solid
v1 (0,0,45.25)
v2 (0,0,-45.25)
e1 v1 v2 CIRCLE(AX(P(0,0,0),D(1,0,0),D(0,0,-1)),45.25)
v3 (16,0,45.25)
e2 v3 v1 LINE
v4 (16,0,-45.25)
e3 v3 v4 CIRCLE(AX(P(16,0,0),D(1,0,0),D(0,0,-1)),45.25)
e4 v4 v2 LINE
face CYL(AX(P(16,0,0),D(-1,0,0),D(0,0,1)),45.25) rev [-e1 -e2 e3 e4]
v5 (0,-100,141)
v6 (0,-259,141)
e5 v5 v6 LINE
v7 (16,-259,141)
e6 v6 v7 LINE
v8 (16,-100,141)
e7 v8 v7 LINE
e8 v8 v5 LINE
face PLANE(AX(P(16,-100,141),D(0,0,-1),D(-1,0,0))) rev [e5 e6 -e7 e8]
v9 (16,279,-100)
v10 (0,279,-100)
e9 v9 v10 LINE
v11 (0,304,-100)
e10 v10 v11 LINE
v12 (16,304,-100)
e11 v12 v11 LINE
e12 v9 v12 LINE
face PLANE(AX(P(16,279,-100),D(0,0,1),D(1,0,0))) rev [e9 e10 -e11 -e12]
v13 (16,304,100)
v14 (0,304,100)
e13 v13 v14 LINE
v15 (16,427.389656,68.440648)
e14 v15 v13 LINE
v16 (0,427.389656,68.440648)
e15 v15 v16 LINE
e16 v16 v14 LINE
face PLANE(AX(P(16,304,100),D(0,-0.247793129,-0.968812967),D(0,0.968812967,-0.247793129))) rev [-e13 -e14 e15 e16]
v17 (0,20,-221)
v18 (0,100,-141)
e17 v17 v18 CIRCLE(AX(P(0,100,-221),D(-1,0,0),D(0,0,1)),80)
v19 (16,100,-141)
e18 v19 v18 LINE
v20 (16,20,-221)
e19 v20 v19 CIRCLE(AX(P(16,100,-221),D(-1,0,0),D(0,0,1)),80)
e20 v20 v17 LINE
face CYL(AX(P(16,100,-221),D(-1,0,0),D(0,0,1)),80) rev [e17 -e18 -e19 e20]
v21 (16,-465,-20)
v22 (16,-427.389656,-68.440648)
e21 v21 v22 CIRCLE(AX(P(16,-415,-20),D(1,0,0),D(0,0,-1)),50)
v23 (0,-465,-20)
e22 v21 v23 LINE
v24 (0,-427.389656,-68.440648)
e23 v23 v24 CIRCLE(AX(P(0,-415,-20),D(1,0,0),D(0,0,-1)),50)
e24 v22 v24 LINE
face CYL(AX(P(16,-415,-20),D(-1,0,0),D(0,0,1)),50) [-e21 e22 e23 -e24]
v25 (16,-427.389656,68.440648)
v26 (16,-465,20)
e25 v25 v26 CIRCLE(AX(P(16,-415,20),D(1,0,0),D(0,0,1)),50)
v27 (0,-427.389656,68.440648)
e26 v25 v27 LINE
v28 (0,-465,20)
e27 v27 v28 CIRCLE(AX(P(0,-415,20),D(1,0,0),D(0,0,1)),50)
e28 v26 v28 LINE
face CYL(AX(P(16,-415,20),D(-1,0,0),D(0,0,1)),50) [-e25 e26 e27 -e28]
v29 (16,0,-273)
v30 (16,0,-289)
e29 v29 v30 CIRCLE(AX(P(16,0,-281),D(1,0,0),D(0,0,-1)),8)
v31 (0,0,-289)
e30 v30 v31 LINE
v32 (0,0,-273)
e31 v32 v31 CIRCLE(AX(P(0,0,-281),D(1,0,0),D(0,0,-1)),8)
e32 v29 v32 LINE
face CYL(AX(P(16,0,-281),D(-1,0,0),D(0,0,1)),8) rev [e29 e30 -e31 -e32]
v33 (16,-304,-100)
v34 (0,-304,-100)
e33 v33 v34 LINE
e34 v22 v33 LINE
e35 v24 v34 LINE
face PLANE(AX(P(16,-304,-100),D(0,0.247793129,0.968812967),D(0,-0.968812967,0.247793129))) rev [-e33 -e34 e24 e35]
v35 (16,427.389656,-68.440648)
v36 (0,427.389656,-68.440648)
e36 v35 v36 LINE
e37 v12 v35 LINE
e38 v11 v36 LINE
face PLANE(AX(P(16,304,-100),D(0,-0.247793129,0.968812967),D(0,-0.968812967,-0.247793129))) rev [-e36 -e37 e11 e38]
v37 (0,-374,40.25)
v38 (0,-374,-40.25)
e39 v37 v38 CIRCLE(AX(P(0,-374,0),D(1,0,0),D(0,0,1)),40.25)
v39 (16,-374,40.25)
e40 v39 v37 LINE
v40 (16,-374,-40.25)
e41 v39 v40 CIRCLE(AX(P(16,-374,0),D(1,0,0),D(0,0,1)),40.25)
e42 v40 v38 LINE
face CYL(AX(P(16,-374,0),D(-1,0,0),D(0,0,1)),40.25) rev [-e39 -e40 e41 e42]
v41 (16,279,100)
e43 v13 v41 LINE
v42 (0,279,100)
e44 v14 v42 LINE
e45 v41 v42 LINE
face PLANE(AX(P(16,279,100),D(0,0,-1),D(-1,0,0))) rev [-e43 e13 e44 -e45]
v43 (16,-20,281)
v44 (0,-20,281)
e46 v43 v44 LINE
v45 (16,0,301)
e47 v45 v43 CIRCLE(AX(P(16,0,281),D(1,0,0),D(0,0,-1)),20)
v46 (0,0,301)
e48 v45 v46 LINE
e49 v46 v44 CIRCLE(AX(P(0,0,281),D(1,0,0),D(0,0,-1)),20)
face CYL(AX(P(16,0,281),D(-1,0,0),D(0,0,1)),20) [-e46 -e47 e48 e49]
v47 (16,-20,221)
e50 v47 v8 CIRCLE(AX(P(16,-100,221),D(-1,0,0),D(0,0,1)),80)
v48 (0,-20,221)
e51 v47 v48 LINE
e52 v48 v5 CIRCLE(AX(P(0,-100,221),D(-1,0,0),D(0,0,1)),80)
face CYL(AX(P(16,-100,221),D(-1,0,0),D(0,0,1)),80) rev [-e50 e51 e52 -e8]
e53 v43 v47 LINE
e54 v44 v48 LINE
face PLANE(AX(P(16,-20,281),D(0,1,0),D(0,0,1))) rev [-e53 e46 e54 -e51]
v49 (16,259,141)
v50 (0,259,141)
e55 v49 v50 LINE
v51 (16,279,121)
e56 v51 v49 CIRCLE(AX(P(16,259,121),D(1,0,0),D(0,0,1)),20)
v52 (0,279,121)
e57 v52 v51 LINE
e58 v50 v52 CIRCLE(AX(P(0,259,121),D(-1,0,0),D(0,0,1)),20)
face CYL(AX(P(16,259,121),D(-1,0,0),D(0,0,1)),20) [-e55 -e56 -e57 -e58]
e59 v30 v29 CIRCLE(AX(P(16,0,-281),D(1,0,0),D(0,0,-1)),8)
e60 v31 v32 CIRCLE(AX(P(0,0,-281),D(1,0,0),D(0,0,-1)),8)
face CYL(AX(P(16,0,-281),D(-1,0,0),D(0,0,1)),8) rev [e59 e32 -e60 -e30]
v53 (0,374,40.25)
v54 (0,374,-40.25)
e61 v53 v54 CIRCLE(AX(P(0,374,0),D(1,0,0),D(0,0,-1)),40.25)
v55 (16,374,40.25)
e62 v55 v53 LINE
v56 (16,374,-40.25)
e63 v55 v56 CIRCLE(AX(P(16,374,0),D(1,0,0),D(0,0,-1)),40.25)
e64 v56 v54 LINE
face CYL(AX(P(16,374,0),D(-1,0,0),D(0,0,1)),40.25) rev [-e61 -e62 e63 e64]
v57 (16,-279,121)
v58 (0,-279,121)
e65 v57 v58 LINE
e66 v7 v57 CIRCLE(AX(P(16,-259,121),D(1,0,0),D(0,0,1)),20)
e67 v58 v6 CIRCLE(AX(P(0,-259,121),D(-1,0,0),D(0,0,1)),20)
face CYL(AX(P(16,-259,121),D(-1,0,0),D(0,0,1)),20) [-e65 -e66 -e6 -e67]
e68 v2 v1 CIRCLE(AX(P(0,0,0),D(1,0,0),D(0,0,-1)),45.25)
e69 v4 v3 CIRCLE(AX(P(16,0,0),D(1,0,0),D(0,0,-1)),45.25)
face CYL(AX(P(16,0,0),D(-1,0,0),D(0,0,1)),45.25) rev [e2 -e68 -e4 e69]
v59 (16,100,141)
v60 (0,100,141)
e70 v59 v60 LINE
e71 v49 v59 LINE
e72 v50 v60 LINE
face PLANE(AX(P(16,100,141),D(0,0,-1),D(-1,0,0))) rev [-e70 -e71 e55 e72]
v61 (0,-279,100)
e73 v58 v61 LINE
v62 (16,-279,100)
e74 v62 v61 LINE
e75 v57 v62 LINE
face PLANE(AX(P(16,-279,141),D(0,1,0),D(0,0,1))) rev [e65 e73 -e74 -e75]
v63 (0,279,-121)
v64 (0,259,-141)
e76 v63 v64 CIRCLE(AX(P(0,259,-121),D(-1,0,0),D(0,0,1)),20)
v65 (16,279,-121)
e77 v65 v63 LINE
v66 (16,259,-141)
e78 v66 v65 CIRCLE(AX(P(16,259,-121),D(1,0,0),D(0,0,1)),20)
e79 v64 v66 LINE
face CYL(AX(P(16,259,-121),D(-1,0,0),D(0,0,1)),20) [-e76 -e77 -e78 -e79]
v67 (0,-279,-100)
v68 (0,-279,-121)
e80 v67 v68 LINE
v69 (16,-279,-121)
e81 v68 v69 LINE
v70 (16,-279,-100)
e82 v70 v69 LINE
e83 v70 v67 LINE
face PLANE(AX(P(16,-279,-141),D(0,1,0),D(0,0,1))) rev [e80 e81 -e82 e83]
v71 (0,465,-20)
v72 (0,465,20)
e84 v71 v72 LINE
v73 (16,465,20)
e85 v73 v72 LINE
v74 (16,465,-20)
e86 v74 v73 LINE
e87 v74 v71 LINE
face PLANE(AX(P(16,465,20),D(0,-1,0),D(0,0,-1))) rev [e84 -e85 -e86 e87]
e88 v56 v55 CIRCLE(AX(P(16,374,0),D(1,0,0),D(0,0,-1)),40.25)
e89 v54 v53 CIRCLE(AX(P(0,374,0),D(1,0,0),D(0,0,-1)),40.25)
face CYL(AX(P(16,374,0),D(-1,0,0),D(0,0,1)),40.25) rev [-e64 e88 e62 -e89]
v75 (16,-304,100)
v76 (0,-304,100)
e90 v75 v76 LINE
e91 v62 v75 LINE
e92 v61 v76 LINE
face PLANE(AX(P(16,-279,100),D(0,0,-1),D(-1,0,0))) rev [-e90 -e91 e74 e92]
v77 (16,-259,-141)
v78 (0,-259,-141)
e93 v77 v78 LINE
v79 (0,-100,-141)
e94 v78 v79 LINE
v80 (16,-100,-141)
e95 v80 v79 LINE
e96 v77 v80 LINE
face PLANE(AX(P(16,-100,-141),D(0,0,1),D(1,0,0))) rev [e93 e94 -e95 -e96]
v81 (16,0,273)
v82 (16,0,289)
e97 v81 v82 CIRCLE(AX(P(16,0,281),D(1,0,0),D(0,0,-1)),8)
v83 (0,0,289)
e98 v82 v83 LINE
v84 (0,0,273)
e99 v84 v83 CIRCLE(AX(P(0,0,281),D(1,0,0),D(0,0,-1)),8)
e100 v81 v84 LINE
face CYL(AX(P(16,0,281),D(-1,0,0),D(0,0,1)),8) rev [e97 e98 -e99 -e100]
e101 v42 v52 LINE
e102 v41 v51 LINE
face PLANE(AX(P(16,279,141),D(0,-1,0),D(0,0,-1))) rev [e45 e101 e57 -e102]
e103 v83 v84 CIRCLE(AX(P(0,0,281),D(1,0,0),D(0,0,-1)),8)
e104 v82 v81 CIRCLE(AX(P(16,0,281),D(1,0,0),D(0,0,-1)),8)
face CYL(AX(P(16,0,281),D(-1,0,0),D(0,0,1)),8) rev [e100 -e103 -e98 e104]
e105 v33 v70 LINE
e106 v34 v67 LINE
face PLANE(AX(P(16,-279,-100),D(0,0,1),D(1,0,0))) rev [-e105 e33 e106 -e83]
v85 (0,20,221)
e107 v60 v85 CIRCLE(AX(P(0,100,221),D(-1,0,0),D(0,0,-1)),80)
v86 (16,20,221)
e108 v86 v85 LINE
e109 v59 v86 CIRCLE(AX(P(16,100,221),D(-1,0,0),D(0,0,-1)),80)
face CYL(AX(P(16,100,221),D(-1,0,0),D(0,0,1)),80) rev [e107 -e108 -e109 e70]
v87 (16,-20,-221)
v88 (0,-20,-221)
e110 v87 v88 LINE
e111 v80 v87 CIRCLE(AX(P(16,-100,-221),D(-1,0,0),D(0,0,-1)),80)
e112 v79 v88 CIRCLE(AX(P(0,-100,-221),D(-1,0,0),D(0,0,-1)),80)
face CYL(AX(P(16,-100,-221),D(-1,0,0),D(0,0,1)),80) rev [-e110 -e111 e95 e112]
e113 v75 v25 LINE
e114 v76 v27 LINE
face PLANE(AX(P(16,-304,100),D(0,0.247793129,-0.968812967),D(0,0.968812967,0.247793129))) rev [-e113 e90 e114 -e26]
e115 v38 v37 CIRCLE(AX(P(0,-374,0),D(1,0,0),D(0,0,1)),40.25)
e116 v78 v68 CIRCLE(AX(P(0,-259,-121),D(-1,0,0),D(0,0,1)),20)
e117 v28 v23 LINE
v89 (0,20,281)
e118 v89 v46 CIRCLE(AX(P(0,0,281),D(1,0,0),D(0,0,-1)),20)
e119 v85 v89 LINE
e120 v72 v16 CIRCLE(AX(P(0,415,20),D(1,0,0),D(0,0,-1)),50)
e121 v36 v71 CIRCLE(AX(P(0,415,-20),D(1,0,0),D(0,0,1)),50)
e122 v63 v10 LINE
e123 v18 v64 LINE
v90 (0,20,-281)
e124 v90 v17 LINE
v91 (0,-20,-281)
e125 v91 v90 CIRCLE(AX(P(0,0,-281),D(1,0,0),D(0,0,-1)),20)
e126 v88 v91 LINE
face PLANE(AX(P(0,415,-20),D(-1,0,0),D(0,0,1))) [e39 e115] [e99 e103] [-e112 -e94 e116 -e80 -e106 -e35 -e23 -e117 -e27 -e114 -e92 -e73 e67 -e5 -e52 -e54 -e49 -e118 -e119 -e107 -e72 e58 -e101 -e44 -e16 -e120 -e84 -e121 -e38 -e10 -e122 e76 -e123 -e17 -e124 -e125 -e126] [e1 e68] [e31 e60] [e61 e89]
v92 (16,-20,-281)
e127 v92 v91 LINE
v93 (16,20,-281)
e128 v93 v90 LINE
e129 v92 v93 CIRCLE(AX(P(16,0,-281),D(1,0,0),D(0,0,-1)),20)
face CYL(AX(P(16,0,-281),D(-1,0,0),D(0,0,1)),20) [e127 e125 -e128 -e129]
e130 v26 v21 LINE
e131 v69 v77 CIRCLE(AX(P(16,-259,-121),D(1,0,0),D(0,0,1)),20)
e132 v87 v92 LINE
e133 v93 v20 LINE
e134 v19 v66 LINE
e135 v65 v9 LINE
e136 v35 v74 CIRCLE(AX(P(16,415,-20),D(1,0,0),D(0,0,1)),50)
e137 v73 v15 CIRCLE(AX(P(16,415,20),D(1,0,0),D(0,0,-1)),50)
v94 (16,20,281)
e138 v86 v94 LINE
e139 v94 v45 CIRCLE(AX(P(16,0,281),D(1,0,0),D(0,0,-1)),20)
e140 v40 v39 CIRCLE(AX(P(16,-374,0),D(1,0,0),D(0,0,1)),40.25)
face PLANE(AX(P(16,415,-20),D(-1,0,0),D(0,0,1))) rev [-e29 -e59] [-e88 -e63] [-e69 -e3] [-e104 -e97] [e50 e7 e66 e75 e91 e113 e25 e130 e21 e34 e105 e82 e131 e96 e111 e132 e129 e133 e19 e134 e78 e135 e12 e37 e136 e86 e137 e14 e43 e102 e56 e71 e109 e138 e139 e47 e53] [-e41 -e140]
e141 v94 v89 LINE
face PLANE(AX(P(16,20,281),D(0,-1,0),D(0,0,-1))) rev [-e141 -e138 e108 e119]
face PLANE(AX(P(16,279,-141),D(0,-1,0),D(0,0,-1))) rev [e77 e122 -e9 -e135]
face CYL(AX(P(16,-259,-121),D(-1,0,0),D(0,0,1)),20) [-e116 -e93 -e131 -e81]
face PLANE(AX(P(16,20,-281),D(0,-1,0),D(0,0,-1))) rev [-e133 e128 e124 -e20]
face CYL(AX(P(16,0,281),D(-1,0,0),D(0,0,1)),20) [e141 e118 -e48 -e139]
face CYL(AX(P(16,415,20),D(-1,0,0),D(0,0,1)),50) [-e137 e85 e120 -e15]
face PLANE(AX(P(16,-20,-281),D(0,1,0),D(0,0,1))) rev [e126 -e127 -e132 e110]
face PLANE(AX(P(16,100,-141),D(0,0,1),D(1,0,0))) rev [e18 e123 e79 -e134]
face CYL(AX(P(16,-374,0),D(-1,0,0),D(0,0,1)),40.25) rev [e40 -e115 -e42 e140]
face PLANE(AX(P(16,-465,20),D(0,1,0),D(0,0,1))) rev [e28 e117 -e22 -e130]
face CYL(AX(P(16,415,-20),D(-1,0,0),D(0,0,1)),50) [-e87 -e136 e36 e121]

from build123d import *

# Parameters (mm, degrees)
SKETCH1_R           = 40.25
SKETCH1_R_2         = 45.25
SKETCH1_R_3         = 4.25
SKETCH1_R_4         = 3.5
SKETCH1_R_5         = 8
BOSS_EXTRUDE1_DEPTH = 16
FILLET1_R           = 20
SKETCH2_R           = 4.25
SKETCH2_R_2         = 3.5
BOSS_EXTRUDE2_DEPTH = 16


with BuildPart() as part:
    # Sketch1 → Boss-Extrude1 (new body)
    with BuildSketch(Plane(origin=(0, 0, 0), x_dir=(0, 0, -1), z_dir=(1, 0, 0))):
        with BuildLine():
            Line((-281, 20), (-221, 20))
            ThreePointArc((-221, 20), (-164.431457505, 43.431457505), (-141, 100))
            Line((-141, 100), (-141, 279))
            Line((-141, 279), (-100, 279))
            Line((-100, 279), (-100, 304))
            Line((-100, 304), (-68.44064835, 427.389656469))
            ThreePointArc((-68.44064835, 427.389656469), (-50.663636253, 454.493561649), (-20, 465))
            Line((-20, 465), (20, 465))
            ThreePointArc((20, 465), (50.663636253, 454.493561649), (68.44064835, 427.389656469))
            Line((68.44064835, 427.389656469), (100, 304))
            Line((100, 304), (100, 279))
            Line((100, 279), (141, 279))
            Line((141, 279), (141, 100))
            ThreePointArc((141, 100), (164.431457505, 43.431457505), (221, 20))
            Line((221, 20), (281, 20))
            ThreePointArc((281, 20), (301, 0), (281, -20))
            Line((281, -20), (221, -20))
            ThreePointArc((221, -20), (164.431457505, -43.431457505), (141, -100))
            Line((141, -100), (141, -279))
            Line((141, -279), (100, -279))
            Line((100, -279), (100, -304))
            Line((100, -304), (68.44064835, -427.389656469))
            ThreePointArc((68.44064835, -427.389656469), (50.663636253, -454.493561649), (20, -465))
            Line((20, -465), (-20, -465))
            ThreePointArc((-20, -465), (-50.663636253, -454.493561649), (-68.44064835, -427.389656469))
            Line((-68.44064835, -427.389656469), (-100, -304))
            Line((-100, -304), (-100, -279))
            Line((-100, -279), (-141, -279))
            Line((-141, -279), (-141, -100))
            ThreePointArc((-141, -100), (-164.431457505, -43.431457505), (-221, -20))
            Line((-221, -20), (-281, -20))
            ThreePointArc((-281, -20), (-301, 0), (-281, 20))
        make_face()
        with Locations((0, 374)):
            Circle(SKETCH1_R, mode=Mode.SUBTRACT)
        Circle(SKETCH1_R_2, mode=Mode.SUBTRACT)
        with Locations(Location((0, -374, 0), (0, 0, 180))):
            Circle(SKETCH1_R, mode=Mode.SUBTRACT)
        with Locations((20, -75)):
            Circle(SKETCH1_R_3, mode=Mode.SUBTRACT)
        with Locations((-20, -75)):
            Circle(SKETCH1_R_3, mode=Mode.SUBTRACT)
        with Locations((-20, 442)):
            Circle(SKETCH1_R_4, mode=Mode.SUBTRACT)
        with Locations((20, 442)):
            Circle(SKETCH1_R_4, mode=Mode.SUBTRACT)
        with Locations(Location((-20, -442, 0), (0, 0, 180))):
            Circle(SKETCH1_R_3, mode=Mode.SUBTRACT)
        with Locations(Location((20, -442, 0), (0, 0, 180))):
            Circle(SKETCH1_R_3, mode=Mode.SUBTRACT)
        with Locations((-281, 0)):
            Circle(SKETCH1_R_5, mode=Mode.SUBTRACT)
        with Locations((281, 0)):
            Circle(SKETCH1_R_5, mode=Mode.SUBTRACT)
    extrude(amount=BOSS_EXTRUDE1_DEPTH)

    # Fillet1
    fillet1_edges = [part.edges().sort_by_distance(p)[0] for p in [
        (8, 279, -141),
        (8, -279, -141),
        (8, -279, 141),
        (8, 279, 141),
    ]]
    fillet(fillet1_edges, radius=FILLET1_R)

    # Sketch2 → Boss-Extrude2 (add)
    with BuildSketch(Plane.ZY):
        with Locations((20, -442)):
            Circle(SKETCH2_R)
        with Locations((-20, -442)):
            Circle(SKETCH2_R)
        with Locations((20, -75)):
            Circle(SKETCH2_R)
        with Locations((-20, -75)):
            Circle(SKETCH2_R)
        with Locations((20, 442)):
            Circle(SKETCH2_R_2)
        with Locations((-20, 442)):
            Circle(SKETCH2_R_2)
    extrude(amount=-BOSS_EXTRUDE2_DEPTH)


solid = part.part
